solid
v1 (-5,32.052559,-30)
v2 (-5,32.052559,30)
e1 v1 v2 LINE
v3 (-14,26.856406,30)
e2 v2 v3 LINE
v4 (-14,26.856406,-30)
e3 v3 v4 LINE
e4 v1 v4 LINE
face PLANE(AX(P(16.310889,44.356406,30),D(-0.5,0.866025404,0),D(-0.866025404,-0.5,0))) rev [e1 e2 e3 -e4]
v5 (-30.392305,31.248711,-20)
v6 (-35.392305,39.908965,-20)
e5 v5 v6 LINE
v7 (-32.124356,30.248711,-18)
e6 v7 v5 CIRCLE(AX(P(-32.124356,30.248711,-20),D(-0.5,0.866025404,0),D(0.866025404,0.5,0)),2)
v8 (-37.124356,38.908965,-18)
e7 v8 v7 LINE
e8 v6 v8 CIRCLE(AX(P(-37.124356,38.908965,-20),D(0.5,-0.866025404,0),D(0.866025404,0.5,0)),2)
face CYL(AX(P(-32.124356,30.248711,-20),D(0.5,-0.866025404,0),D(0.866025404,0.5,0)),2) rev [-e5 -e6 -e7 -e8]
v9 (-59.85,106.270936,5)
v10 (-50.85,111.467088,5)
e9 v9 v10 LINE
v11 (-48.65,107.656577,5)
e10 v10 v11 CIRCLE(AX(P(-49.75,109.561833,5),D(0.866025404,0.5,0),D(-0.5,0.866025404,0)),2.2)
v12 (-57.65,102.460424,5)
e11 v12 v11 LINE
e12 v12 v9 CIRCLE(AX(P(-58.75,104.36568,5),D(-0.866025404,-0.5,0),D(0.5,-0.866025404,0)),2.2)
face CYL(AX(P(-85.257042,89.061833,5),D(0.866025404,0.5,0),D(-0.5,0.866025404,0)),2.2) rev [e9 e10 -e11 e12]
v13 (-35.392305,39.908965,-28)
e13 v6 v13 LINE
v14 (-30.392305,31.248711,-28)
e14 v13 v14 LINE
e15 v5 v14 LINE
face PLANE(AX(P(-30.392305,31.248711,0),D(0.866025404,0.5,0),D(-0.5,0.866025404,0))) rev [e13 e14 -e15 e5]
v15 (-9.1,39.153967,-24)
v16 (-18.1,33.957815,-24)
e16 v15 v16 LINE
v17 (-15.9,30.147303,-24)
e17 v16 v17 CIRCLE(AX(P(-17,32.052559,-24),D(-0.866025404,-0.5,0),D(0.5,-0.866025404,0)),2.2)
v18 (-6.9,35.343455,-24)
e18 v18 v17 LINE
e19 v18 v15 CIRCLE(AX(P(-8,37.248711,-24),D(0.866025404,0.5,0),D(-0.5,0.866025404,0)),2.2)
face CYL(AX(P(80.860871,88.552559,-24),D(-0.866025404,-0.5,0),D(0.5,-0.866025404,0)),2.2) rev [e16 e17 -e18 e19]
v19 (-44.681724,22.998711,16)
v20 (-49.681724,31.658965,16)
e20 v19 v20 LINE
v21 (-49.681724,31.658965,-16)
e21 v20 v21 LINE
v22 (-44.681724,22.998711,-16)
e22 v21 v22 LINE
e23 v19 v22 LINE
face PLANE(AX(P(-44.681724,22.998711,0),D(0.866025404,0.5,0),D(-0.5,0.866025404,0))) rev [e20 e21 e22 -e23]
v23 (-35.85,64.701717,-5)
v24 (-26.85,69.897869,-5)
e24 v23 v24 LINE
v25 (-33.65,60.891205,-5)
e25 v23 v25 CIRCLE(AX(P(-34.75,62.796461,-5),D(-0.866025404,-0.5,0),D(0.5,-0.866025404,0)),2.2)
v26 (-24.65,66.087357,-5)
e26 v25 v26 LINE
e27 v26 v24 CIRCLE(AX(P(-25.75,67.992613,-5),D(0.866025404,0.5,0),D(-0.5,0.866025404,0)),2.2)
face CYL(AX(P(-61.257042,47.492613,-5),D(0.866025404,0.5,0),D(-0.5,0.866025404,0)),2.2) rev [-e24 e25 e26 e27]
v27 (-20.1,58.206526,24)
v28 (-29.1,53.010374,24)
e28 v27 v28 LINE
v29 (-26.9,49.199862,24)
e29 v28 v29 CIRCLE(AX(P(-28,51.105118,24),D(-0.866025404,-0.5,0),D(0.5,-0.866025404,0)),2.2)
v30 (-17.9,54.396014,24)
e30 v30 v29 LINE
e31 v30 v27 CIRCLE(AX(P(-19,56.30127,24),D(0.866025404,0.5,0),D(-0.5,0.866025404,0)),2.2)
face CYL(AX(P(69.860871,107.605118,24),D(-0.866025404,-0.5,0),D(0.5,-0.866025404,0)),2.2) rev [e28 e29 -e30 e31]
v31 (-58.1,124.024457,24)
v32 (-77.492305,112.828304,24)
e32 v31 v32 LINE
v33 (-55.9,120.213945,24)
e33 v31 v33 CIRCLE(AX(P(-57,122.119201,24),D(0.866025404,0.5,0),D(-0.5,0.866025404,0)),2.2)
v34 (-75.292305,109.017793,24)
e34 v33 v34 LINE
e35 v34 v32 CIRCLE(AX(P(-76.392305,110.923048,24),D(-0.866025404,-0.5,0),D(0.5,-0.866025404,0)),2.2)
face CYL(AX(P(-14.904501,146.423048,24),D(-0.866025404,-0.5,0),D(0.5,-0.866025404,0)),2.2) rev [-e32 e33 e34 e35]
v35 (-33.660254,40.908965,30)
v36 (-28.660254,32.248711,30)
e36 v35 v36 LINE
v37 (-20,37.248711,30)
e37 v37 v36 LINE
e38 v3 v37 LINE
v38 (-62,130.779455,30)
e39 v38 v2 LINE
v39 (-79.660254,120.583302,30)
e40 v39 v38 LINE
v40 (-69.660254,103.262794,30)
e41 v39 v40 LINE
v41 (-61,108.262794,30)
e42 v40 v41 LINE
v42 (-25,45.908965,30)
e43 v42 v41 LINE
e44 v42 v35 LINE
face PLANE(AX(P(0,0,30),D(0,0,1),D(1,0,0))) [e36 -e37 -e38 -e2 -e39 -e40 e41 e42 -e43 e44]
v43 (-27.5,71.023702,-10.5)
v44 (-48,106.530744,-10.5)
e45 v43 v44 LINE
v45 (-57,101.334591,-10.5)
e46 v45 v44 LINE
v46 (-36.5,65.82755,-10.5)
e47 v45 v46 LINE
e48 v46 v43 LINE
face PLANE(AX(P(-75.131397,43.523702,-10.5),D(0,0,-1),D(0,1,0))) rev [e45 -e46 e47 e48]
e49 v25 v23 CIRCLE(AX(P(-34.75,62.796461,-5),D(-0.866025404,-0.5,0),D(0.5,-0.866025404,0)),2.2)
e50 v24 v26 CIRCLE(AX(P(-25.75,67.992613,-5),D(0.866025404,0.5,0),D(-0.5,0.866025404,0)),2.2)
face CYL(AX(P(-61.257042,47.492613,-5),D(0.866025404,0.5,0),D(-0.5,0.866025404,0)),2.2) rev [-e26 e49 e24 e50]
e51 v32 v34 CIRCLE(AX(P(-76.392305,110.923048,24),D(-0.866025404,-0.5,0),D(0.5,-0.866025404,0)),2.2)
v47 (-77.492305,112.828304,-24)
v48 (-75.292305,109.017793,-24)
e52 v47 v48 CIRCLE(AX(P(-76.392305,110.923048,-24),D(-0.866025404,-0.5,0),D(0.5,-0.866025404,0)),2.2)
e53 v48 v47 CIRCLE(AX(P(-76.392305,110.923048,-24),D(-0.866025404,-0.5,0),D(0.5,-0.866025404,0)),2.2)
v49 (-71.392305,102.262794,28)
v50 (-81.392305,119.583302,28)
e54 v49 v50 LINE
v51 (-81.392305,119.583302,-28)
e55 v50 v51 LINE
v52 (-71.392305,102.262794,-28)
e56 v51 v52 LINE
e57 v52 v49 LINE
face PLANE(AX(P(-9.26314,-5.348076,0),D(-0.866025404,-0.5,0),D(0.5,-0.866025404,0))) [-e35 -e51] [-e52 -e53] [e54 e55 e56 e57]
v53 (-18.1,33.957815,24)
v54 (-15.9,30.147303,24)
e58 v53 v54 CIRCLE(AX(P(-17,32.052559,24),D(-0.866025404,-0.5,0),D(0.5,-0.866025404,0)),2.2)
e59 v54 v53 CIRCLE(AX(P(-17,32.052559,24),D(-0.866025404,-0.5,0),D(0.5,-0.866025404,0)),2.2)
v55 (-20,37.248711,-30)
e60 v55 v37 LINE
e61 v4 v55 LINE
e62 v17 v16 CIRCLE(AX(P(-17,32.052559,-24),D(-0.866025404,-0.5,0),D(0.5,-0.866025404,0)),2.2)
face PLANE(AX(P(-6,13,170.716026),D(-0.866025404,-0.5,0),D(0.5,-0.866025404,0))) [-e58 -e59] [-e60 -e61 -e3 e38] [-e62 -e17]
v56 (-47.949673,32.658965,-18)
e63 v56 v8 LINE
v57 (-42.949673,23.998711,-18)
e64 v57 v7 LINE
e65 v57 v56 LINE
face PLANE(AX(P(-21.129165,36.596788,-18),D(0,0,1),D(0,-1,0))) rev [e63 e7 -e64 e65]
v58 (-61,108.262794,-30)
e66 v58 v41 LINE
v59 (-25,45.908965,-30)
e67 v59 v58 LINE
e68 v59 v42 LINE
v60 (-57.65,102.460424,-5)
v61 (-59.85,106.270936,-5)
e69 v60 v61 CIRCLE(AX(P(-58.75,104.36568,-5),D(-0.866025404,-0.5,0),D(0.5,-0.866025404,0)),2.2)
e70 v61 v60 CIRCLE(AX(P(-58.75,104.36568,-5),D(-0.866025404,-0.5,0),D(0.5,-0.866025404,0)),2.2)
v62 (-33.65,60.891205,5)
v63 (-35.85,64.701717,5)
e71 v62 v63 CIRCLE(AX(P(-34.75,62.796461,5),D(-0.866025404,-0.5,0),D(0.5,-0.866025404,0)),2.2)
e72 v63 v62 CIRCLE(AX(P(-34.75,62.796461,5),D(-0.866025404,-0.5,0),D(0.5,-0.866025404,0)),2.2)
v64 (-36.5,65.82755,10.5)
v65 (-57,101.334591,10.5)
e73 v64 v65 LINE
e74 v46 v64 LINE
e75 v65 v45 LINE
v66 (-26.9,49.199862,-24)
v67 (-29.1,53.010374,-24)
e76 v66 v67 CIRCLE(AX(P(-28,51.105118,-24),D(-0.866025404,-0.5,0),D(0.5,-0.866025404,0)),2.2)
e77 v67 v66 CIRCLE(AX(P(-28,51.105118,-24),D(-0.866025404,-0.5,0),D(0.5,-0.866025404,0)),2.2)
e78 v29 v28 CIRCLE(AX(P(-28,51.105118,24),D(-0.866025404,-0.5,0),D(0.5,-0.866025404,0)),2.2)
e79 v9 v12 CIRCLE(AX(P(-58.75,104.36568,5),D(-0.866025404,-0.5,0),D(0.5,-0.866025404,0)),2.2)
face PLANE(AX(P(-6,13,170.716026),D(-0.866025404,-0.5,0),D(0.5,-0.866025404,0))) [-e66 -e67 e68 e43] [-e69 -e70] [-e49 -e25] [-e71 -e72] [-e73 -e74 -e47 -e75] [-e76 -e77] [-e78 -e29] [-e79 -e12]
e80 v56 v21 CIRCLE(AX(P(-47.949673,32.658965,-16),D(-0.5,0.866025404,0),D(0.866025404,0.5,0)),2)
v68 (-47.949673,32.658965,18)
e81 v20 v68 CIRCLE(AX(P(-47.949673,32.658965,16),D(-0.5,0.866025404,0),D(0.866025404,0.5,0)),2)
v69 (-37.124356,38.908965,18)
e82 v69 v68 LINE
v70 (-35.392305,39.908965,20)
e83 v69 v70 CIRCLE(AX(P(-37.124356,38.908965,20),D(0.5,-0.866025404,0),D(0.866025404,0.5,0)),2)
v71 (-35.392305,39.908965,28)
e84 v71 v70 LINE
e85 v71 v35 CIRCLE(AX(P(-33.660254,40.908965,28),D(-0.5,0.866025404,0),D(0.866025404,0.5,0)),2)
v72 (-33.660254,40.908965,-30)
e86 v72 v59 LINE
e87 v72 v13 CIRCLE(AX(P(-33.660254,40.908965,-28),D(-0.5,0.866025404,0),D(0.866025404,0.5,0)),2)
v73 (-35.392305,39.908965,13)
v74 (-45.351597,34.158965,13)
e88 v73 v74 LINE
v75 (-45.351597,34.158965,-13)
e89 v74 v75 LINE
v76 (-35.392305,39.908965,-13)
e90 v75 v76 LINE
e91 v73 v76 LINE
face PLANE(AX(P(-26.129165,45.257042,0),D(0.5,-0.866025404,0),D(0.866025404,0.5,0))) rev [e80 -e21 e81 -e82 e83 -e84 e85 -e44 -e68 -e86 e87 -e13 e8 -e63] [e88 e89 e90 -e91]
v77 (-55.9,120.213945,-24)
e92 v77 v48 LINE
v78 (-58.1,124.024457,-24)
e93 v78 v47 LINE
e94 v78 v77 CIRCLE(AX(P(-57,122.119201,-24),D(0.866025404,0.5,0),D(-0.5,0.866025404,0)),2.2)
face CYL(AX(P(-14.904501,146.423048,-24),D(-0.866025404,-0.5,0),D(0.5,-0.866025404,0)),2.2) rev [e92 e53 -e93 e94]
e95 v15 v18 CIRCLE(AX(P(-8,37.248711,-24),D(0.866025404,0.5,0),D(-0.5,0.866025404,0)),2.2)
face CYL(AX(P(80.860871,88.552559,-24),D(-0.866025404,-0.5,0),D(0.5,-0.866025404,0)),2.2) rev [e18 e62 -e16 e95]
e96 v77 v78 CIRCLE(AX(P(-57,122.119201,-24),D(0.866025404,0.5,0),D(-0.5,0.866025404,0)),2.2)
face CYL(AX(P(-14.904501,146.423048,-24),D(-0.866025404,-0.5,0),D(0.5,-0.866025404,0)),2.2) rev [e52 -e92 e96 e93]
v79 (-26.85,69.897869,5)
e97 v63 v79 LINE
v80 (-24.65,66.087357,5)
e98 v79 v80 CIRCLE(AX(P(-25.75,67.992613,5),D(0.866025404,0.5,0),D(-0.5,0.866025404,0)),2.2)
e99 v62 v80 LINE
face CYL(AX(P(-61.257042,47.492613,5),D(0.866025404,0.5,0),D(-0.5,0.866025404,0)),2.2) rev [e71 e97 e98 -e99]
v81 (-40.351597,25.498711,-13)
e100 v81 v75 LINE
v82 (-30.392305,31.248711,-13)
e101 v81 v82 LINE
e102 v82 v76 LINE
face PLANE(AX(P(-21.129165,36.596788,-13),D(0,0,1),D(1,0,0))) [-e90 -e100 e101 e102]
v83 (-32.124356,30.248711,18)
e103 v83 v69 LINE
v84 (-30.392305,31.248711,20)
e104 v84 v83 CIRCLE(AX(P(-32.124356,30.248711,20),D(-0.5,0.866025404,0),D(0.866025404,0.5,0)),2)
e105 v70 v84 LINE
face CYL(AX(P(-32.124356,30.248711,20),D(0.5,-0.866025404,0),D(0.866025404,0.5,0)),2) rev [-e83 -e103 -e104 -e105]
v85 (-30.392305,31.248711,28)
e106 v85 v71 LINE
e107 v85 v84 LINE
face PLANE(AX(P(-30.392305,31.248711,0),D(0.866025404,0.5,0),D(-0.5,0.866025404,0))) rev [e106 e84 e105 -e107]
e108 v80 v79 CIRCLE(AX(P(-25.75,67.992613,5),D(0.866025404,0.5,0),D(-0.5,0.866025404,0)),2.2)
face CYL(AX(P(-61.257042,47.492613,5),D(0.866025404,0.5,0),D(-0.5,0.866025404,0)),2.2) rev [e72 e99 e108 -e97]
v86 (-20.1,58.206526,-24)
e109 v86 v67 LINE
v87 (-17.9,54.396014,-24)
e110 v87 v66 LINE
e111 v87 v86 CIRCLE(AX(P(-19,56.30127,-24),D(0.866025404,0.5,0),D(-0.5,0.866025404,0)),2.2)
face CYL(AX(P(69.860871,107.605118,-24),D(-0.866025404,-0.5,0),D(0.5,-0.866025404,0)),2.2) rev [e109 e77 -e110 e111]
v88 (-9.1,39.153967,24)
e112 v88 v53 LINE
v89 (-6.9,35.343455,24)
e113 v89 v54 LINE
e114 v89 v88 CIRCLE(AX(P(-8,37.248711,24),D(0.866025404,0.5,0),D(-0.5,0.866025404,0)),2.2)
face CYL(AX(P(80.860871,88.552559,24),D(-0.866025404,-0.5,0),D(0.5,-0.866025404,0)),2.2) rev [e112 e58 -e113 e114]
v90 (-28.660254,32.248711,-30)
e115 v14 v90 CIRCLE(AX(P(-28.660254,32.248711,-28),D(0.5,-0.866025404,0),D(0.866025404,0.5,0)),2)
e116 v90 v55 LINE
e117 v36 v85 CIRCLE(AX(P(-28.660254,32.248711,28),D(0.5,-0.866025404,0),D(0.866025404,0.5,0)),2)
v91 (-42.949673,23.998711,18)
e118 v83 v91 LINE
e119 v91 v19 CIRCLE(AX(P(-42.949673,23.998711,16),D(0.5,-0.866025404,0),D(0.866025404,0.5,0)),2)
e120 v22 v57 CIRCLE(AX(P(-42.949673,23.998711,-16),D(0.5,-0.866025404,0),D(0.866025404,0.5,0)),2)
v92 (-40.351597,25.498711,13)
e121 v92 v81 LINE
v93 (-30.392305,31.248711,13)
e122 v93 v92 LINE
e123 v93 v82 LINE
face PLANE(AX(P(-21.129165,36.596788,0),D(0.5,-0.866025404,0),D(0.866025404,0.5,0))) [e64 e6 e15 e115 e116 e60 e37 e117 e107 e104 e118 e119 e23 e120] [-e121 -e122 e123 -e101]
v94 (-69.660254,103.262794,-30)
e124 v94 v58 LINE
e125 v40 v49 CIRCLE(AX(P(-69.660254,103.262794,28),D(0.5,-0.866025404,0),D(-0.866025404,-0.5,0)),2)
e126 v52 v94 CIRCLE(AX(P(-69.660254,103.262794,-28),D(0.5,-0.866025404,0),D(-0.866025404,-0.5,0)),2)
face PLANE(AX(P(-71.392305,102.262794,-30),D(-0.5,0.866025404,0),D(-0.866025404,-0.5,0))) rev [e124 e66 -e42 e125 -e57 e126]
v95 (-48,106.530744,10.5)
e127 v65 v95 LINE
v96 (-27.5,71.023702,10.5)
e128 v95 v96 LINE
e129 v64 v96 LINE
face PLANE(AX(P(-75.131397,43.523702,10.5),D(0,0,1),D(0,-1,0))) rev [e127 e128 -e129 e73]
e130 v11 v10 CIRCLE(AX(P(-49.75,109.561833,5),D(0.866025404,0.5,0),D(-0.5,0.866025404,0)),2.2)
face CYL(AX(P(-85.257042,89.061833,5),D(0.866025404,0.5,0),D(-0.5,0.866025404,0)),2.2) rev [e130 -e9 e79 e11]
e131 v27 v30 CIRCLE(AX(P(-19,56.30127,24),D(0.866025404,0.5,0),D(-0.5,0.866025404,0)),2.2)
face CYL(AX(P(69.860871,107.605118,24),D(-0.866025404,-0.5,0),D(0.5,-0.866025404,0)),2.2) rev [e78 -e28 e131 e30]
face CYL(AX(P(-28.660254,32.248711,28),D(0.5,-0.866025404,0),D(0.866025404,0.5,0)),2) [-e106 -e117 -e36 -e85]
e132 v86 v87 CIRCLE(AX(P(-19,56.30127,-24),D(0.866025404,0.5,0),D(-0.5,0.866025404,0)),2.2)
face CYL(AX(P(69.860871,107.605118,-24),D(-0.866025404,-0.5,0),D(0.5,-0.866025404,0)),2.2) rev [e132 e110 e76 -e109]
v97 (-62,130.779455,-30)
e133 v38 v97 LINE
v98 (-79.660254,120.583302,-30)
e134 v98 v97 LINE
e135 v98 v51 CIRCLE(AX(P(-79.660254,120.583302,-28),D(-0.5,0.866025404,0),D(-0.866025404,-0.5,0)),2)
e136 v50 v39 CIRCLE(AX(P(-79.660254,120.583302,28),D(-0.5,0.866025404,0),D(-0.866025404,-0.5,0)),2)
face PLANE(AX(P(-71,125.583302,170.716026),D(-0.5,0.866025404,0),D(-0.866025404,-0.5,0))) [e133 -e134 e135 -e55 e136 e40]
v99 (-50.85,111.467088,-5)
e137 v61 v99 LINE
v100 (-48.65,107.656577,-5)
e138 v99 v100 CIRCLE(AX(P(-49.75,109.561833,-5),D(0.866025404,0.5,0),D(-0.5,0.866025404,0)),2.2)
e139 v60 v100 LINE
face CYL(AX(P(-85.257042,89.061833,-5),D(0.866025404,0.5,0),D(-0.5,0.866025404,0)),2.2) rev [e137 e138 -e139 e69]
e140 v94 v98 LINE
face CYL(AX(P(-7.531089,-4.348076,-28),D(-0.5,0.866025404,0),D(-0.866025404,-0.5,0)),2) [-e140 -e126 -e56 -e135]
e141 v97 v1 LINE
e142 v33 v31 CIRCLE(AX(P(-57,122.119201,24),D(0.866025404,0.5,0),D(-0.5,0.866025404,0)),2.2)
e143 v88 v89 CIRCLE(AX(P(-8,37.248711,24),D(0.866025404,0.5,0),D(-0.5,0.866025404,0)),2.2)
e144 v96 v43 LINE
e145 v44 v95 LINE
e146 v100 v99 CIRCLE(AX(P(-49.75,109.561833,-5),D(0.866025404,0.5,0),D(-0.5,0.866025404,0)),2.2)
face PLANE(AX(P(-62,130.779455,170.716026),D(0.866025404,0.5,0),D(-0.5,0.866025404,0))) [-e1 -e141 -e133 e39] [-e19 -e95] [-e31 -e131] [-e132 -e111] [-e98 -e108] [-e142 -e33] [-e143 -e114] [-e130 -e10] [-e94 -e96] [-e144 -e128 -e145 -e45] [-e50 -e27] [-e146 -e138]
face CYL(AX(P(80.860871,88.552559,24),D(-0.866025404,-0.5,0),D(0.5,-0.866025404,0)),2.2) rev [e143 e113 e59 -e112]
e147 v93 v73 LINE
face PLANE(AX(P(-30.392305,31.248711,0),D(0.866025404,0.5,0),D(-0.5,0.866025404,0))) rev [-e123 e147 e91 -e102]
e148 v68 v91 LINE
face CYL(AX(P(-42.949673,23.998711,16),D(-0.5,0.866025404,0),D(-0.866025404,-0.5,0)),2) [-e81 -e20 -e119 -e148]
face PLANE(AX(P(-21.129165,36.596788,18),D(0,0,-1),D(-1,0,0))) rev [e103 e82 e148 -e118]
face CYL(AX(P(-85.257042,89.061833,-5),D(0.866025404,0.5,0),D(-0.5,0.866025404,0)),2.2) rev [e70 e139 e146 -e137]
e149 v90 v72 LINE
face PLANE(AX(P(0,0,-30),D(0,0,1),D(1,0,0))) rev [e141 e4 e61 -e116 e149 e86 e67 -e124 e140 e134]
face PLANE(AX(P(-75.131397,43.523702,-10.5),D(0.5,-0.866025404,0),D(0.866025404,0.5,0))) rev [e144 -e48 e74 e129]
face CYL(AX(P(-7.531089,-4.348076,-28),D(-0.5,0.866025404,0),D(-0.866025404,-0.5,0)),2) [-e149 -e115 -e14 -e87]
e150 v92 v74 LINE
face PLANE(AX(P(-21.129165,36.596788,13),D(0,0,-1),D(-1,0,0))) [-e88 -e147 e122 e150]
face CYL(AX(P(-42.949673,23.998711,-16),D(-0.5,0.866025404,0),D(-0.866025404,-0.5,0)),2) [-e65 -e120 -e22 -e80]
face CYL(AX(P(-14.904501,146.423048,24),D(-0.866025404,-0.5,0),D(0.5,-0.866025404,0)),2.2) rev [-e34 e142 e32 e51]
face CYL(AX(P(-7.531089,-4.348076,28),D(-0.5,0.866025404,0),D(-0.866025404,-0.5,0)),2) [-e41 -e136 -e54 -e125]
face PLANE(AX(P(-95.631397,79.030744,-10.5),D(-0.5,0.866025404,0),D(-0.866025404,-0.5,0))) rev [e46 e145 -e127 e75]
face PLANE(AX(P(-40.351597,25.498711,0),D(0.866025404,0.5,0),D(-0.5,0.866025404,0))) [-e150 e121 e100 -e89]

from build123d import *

# Parameters (mm, degrees)
SKETCH_1_W          = 12
SKETCH_1_H          = 26
EXTRUDE_1_DEPTH     = 30
EXTRUDE_2_DEPTH     = 60
SKETCH_3_W          = 60
SKETCH_3_H          = 20
EXTRUDE_3_DEPTH     = 12
EXTRUDE_START       = 72
SKETCH_5_W          = 26
SKETCH_5_H          = 11.5
EXTRUDE_4_DEPTH     = 10
SKETCH_6_W          = 21
SKETCH_6_H          = 41
CUT_EXTRUDE_1_DEPTH = 55
SKETCH_7_R          = 2.2
CUT_EXTRUDE_2_DEPTH = 41
FILLET_1_R          = 20
SKETCH_8_R          = 3.3
CUT_EXTRUDE_3_DEPTH = 21
FILLET_2_R          = 2
FILLET_3_R          = 2
FILLET_4_R          = 2
SKETCH_9_W          = 60
SKETCH_9_H          = 60.516660498
CUT_EXTRUDE_4_DEPTH = 35
SKETCH_10_R         = 2.2
CUT_EXTRUDE_5_DEPTH = 71
SKETCH_12_R         = 2.2
CUT_EXTRUDE_6_DEPTH = 113


with BuildPart() as part:
    # 草图1 → 凸台-拉伸1 (new, symmetric)
    with BuildSketch(Plane.XY):
        Rectangle(SKETCH_1_W, SKETCH_1_H)
    extrude(amount=EXTRUDE_1_DEPTH, both=True)

    # 草图2 → 凸台-拉伸2 (add)
    with BuildSketch(Plane(origin=(0, 0, -30), x_dir=(-1, 0, 0), z_dir=(0, 0, -1))):
        Polygon((6, 13), (71, 125.583302492), (62, 130.779454915), (-6, 13), align=None)
    extrude(amount=-EXTRUDE_2_DEPTH)

    # 草图3 → 凸台-拉伸3 (add)
    with BuildSketch(Plane(origin=(1.129165125, 0.651923789, 0), x_dir=(0, 0, 1), z_dir=(-0.866025403784438, -0.500000000000001, 0))):
        with Locations((0, 134.258330249)):
            Rectangle(SKETCH_3_W, SKETCH_3_H)
    extrude(amount=EXTRUDE_3_DEPTH)

    # 草图5 → 凸台-拉伸4 (add)
    with BuildSketch(Plane(origin=(-62.129165125, 107.610870628, 0), x_dir=(0, 0, -1), z_dir=(0.500000000000001, -0.866025403784438, 0)).offset(EXTRUDE_START)):
        Polygon((30, -10.696152423), (30, 1.303847577), (-30, 1.303847577), (-30, -10.696152423), (-18, -10.696152423), (-18, -27.196152423), (18, -27.196152423), (18, -10.696152423), align=None)
        with Locations((0, -16.446152423)):
            Rectangle(SKETCH_5_W, SKETCH_5_H, mode=Mode.SUBTRACT)
    extrude(amount=EXTRUDE_4_DEPTH)

    # 草图6 → 切除-拉伸1 (cut)
    with BuildSketch(Plane(origin=(10.129165125, 5.848076211, 0), x_dir=(0, 0, -1), z_dir=(0.8660254037844382, 0.500000000000001, 0))):
        with Locations((0, 95.758330249)):
            Rectangle(SKETCH_6_W, SKETCH_6_H)
    extrude(amount=-CUT_EXTRUDE_1_DEPTH, mode=Mode.SUBTRACT)

    # 草图7 → 切除-拉伸2 (cut)
    with BuildSketch(Plane(origin=(10.129165125, 5.848076211, 0), x_dir=(0, 0, -1), z_dir=(0.8660254037844382, 0.500000000000001, 0))):
        with Locations(Location((5, 71.758330249, 0), (0, 0, 90))):
            Circle(SKETCH_7_R)
        with Locations(Location((-5, 71.758330249, 0), (0, 0, 90))):
            Circle(SKETCH_7_R)
        with Locations(Location((5, 119.758330249, 0), (0, 0, 90))):
            Circle(SKETCH_7_R)
        with Locations(Location((-5, 119.758330249, 0), (0, 0, 90))):
            Circle(SKETCH_7_R)
    extrude(amount=-CUT_EXTRUDE_2_DEPTH, mode=Mode.SUBTRACT)

    # 圆角1
    fillet_1_edges = [part.edges().sort_by_distance(p)[0] for p in [
        (-6, 13, 0),
        (6, 13, 0),
    ]]
    fillet(fillet_1_edges, radius=FILLET_1_R)

    # 草图8 → 切除-拉伸3 (cut)
    with BuildSketch(Plane.ZY.offset(6)):
        with Locations((-12.5, -3)):
            Circle(SKETCH_8_R)
        with Locations((12.5, -3)):
            Circle(SKETCH_8_R)
    extrude(amount=-CUT_EXTRUDE_3_DEPTH, mode=Mode.SUBTRACT)

    # 圆角2
    fillet_2_edges = [part.edges().sort_by_distance(p)[0] for p in [
        (0, -13, 30),
        (0, -13, -30),
    ]]
    fillet(fillet_2_edges, radius=FILLET_2_R)

    # 圆角3
    fillet_3_edges = [part.edges().sort_by_distance(p)[0] for p in [
        (-32.892304845, 35.578838325, -30),
        (-32.892304845, 35.578838325, 30),
        (-32.892304845, 35.578838325, 18),
        (-47.181724008, 27.328838325, 18),
        (-47.181724008, 27.328838325, -18),
        (-32.892304845, 35.578838325, -18),
    ]]
    fillet(fillet_3_edges, radius=FILLET_3_R)

    # 圆角4
    fillet_4_edges = [part.edges().sort_by_distance(p)[0] for p in [
        (-76.392304845, 110.923048454, 30),
        (-76.392304845, 110.923048454, -30),
    ]]
    fillet(fillet_4_edges, radius=FILLET_4_R)

    # 草图9 → 切除-拉伸4 (cut, symmetric)
    with BuildSketch(Plane(origin=(1.129165125, 0.651923789, 0), x_dir=(0, 0, 1), z_dir=(-0.8660254037844382, -0.500000000000001, 0))):
        Rectangle(SKETCH_9_W, SKETCH_9_H)
    extrude(amount=CUT_EXTRUDE_4_DEPTH, both=True, mode=Mode.SUBTRACT)

    # 草图10 → 切除-拉伸5 (cut)
    with BuildSketch(Plane(origin=(-9.263139721, -5.348076211, 0), x_dir=(0, 0, 1), z_dir=(-0.866025403784438, -0.5000000000000009, 0))):
        with Locations(Location((24, 134.258330249, 0), (0, 0, 270))):
            Circle(SKETCH_10_R)
        with Locations(Location((-24, 134.258330249, 0), (0, 0, 270))):
            Circle(SKETCH_10_R)
    extrude(amount=-CUT_EXTRUDE_5_DEPTH, mode=Mode.SUBTRACT)

    # 草图12 → 切除-拉伸6 (cut)
    with BuildSketch(Plane(origin=(1.129165125, 0.651923789, 0), x_dir=(0, 0, 1), z_dir=(-0.8660254037844382, -0.500000000000001, 0))):
        with Locations(Location((-24, 58.258330249, 0), (0, 0, 270))):
            Circle(SKETCH_12_R)
        with Locations(Location((24, 58.258330249, 0), (0, 0, 270))):
            Circle(SKETCH_12_R)
        with Locations(Location((24, 36.258330249, 0), (0, 0, 270))):
            Circle(SKETCH_12_R)
        with Locations(Location((-24, 36.258330249, 0), (0, 0, 270))):
            Circle(SKETCH_12_R)
    extrude(amount=-CUT_EXTRUDE_6_DEPTH, mode=Mode.SUBTRACT)


solid = part.part
